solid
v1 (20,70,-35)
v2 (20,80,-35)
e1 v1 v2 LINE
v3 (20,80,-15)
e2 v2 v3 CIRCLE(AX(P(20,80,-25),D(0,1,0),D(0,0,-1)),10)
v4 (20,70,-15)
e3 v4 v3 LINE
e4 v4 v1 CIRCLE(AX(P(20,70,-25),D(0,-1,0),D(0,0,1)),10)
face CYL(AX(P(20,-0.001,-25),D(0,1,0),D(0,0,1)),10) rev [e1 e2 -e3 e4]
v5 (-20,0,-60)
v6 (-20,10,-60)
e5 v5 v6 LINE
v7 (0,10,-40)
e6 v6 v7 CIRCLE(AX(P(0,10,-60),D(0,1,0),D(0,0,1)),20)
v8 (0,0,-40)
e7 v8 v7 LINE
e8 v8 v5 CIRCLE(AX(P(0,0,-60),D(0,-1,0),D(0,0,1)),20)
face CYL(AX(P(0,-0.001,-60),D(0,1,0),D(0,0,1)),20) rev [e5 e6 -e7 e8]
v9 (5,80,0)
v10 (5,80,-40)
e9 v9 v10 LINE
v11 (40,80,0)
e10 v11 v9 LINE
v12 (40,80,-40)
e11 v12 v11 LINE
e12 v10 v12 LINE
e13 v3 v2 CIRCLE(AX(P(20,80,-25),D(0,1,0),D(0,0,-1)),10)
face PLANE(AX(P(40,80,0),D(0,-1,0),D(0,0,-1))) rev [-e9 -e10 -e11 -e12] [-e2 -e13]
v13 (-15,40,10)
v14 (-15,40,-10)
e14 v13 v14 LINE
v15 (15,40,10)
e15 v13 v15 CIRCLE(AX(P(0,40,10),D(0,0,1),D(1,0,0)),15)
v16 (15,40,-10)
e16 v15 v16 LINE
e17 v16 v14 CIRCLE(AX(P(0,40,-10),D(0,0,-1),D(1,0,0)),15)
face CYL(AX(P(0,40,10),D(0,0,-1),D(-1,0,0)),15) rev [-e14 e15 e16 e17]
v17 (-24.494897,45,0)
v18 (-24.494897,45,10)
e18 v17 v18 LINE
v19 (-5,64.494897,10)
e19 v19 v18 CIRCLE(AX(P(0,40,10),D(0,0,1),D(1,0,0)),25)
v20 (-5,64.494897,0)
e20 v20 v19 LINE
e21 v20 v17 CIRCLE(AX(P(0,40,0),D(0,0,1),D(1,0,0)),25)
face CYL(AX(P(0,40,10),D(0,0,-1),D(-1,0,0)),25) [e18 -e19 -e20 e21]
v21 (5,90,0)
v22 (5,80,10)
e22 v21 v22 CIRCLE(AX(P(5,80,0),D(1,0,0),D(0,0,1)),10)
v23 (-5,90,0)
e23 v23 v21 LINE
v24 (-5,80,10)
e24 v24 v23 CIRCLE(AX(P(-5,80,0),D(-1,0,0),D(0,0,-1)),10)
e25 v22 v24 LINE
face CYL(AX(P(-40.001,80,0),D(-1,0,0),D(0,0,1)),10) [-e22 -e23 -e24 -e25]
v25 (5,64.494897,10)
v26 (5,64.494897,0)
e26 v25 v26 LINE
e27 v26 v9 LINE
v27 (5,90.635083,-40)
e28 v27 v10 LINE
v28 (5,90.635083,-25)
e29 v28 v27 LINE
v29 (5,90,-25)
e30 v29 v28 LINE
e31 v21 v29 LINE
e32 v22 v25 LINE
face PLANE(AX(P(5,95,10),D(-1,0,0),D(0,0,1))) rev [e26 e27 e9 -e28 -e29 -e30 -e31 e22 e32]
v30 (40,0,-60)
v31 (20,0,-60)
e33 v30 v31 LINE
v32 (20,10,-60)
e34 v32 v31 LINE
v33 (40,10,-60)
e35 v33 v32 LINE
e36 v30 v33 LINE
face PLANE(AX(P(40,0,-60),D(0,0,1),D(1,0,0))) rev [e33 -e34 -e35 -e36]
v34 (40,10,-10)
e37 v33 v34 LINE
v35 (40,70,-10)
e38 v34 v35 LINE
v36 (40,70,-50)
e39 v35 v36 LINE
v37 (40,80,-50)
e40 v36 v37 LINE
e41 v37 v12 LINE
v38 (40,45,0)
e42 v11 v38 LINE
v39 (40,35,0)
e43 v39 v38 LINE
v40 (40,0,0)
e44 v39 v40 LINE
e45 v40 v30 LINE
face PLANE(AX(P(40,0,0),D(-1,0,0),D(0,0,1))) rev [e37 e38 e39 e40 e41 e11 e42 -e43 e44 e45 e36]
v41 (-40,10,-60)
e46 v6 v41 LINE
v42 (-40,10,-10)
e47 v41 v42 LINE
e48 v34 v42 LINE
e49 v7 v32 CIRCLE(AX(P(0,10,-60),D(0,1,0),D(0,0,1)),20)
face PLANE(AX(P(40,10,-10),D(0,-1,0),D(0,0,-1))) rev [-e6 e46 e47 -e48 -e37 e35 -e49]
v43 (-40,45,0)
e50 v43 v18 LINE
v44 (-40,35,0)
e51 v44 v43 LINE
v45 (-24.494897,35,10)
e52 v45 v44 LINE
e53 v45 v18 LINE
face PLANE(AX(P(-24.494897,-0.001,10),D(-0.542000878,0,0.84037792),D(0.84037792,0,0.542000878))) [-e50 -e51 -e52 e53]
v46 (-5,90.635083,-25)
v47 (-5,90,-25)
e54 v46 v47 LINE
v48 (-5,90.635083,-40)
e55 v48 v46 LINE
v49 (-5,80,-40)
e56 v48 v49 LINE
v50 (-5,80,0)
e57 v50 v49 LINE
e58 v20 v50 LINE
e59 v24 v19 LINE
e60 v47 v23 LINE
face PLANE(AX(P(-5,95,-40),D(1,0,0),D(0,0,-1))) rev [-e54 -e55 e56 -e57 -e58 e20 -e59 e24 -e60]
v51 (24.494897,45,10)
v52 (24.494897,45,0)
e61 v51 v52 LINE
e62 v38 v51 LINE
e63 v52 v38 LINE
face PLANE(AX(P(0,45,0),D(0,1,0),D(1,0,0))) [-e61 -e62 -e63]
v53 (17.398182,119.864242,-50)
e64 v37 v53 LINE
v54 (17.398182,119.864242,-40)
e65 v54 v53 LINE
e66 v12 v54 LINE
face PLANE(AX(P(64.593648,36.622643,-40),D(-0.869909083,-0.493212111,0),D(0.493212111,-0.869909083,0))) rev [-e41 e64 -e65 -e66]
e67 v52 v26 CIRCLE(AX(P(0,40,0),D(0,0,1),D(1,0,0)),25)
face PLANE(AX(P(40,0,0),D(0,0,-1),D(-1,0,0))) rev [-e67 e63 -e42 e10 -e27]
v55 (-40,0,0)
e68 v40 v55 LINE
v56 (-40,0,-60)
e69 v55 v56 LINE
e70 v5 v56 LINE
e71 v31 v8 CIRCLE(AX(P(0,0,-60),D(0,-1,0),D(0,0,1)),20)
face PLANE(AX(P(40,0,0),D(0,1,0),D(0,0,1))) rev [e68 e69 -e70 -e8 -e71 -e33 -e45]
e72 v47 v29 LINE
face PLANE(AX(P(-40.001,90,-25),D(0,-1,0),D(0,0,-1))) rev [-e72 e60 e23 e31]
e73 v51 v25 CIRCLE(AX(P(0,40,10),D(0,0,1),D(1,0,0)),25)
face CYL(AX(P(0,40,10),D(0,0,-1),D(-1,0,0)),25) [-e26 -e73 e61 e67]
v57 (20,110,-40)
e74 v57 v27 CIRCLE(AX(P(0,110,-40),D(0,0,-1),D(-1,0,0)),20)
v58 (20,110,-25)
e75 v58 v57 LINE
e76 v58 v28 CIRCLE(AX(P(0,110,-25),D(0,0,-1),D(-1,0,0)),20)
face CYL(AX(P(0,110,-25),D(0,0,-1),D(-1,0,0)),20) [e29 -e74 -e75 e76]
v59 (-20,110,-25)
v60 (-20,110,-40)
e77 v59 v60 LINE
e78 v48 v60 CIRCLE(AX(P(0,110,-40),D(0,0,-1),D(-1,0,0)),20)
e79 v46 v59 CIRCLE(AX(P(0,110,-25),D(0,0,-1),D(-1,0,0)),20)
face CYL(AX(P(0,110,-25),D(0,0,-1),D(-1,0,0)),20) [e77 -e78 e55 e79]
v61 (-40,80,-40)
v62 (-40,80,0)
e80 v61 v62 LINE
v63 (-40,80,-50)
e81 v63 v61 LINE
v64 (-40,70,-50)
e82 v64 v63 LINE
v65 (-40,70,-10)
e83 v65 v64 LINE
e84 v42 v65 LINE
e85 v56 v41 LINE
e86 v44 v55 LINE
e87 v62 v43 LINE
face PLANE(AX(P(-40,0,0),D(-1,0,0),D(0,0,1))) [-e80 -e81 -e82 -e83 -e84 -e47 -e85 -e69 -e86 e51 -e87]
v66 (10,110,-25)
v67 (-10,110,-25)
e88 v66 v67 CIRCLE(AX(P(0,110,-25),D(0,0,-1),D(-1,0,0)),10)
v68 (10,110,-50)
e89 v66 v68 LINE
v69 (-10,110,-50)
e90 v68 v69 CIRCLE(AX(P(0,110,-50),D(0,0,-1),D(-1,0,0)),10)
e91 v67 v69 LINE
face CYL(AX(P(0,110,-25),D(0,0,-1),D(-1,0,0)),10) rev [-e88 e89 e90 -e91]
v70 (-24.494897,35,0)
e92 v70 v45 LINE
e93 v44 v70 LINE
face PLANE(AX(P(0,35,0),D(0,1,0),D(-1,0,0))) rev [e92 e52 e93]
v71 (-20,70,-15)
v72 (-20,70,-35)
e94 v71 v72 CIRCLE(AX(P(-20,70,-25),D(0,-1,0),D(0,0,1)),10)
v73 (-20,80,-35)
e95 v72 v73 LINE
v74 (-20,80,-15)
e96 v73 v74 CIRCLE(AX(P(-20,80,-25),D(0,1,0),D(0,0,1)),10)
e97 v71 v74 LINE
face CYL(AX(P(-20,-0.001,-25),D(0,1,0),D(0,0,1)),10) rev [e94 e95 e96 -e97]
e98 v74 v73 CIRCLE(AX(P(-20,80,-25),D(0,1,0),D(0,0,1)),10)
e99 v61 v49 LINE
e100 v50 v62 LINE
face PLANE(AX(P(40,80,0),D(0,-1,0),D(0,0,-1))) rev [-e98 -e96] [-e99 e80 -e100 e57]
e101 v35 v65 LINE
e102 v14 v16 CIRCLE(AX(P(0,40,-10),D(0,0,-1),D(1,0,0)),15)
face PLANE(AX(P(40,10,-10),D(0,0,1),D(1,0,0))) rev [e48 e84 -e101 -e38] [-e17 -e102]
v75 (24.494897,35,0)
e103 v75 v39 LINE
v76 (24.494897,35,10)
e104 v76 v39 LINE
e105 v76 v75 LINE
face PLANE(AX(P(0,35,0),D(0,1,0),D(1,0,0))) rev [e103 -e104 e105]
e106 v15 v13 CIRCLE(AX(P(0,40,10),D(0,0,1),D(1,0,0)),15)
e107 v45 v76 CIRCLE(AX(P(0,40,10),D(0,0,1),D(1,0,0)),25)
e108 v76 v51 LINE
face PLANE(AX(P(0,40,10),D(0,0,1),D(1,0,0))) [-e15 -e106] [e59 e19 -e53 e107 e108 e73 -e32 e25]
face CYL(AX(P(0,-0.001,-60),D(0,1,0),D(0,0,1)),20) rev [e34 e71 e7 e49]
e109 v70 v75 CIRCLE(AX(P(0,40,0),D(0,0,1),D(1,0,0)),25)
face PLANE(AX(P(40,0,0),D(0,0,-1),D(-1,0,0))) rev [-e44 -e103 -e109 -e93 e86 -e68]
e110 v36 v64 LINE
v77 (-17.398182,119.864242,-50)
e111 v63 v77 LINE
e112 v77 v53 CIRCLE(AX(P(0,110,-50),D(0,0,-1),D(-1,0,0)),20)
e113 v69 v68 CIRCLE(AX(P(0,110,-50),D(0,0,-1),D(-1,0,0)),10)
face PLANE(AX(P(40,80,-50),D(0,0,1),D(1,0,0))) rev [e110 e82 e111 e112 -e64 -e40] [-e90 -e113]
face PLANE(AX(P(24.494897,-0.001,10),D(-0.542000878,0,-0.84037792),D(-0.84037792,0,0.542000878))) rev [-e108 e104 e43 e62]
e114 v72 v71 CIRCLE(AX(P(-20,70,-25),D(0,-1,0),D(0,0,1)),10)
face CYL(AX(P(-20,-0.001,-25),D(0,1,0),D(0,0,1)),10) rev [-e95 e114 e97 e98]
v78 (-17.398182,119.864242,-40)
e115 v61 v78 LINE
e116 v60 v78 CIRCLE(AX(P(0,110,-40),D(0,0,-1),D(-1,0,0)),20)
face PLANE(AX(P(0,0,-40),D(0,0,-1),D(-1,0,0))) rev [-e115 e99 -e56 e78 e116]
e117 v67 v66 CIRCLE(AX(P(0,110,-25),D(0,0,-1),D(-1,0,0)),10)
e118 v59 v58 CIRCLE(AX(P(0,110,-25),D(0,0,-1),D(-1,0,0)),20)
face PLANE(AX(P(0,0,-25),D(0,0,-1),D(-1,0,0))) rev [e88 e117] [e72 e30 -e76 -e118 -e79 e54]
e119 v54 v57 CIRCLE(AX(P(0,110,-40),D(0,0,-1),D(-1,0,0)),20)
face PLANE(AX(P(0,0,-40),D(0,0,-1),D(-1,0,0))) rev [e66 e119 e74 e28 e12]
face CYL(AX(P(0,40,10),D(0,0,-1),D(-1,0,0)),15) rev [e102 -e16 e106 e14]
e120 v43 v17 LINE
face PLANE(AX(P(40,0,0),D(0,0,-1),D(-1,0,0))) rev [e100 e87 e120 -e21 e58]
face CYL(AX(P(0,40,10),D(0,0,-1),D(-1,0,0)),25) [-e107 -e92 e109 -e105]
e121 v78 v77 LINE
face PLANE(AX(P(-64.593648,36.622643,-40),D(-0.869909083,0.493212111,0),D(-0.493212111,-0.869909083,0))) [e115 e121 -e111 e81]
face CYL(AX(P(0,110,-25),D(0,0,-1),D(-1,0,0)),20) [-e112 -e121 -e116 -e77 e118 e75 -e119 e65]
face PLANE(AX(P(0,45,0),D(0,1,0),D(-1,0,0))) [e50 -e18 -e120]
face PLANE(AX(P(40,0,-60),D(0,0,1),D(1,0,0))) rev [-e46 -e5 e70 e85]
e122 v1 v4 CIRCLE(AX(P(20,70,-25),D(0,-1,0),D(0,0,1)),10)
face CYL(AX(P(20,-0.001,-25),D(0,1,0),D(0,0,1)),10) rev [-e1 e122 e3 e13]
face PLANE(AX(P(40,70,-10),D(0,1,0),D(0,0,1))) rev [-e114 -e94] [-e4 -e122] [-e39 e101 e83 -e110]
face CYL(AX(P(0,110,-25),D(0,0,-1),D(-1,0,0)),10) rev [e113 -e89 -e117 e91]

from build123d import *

# Parameters (mm, degrees)
BASE_BRACKET_80MM_DEPTH   = 40
UPPER_LUG_PLATE_DEPTH     = 10
SKETCH2_3_R               = 20
SKETCH2_3_R_2             = 10
UPPER_LUG_HUB_DEPTH       = 25
FRONT_LUG_PROFILE_R       = 25
FRONT_LUG_PROFILE_R_2     = 15
FRONT_LUG_BOSS_DEPTH      = 10
FRONT_LUG_BORE_REACH      = 150.661
SKETCH4_2_R               = 15
CONNECTING_WEB_DEPTH      = 5
WEB_PAD_A_PROFILE_W       = 10
WEB_PAD_A_PROFILE_H       = 10
WEB_PAD_A_DEPTH           = 5
WEB_PAD_B_PROFILE_W       = 10
WEB_PAD_B_PROFILE_H       = 50
WEB_PAD_B_DEPTH           = 5
WEB_RELIEF_CUT_REACH      = 152.083
WEB_RELIEF_PROFILE_W      = 35
WEB_RELIEF_PROFILE_H      = 5
WEB_RELIEF_FILLET_R10_R   = 10
GUSSET_RIB_DEPTH          = 5
RIB_TRIM_CUT_REACH        = 113.467
RIB_PAD_A_DEPTH           = 5
RIB_PAD_B_DEPTH           = 5
LUG_CLEARANCE_CUT_REACH   = 154.971
RIB_NOTCH_CUT_DEPTH       = 10
UPPER_HUB_BORE_20_REACH   = 109.703
UPPER_HUB_BORE_PROFILE_R  = 10
BASE_ARC_CUTOUT_REACH     = 142
BASE_ARC_CUTOUT_PROFILE_R = 20


with BuildPart() as part:
    # Base Bracket Profile → Base Bracket 80mm (new, symmetric)
    with BuildSketch(Plane(origin=(0, 0, 0), x_dir=(0, 0, -1), z_dir=(1, 0, 0))):
        Polygon((0, 0), (60, 0), (60, 10), (10, 10), (10, 70), (50, 70), (50, 80), (0, 80), align=None)
    extrude(amount=BASE_BRACKET_80MM_DEPTH, both=True)

    # Upper Lug Profile → Upper Lug Plate (add)
    with BuildSketch(Plane(origin=(0, 0, -50), x_dir=(-1, 0, 0), z_dir=(0, 0, -1))):
        with BuildLine():
            Line((-40, 80), (0, 80))
            Line((0, 80), (0, 90))
            ThreePointArc((0, 90), (-17.281273745, 99.932349938), (-17.398181668, 119.864242224))
            Line((-17.398181668, 119.864242224), (-40, 80))
        make_face()
        with BuildLine():
            Line((0, 90), (0, 80))
            Line((0, 80), (40, 80))
            Line((40, 80), (17.398181668, 119.864242224))
            ThreePointArc((17.398181668, 119.864242224), (19.338609482, 115.100802223), (20, 110))
            ThreePointArc((20, 110), (14.142135624, 95.857864376), (0, 90))
        make_face()
    extrude(amount=-UPPER_LUG_PLATE_DEPTH)

    # Sketch2_3 → Upper Lug Hub (add)
    with BuildSketch(Plane(origin=(0, 0, -50), x_dir=(-1, 0, 0), z_dir=(0, 0, -1))):
        with Locations((0, 110)):
            Circle(SKETCH2_3_R)
        with Locations((0, 110)):
            Circle(SKETCH2_3_R_2, mode=Mode.SUBTRACT)
    extrude(amount=-UPPER_LUG_HUB_DEPTH)

    # Front Lug Profile → Front Lug Boss (add)
    with BuildSketch(Plane.XY):
        with Locations((0, 40)):
            Circle(FRONT_LUG_PROFILE_R)
        with Locations((0, 40)):
            Circle(FRONT_LUG_PROFILE_R_2, mode=Mode.SUBTRACT)
    extrude(amount=FRONT_LUG_BOSS_DEPTH)

    # Sketch4_2 → Front Lug Bore (cut, up to next)
    with BuildSketch(Plane.XY, mode=Mode.PRIVATE) as front_lug_bore_sk1:
        with Locations((0, 40)):
            Circle(SKETCH4_2_R)
    front_lug_bore_tool1 = extrude(front_lug_bore_sk1.sketch, amount=-FRONT_LUG_BORE_REACH, mode=Mode.PRIVATE) & part.part
    add(front_lug_bore_tool1.solids().sort_by_distance((0, 40, 0))[0], mode=Mode.SUBTRACT)



with BuildPart() as body_2:
    # Connecting Web Profile → Connecting Web (new, symmetric)
    with BuildSketch(Plane(origin=(0, 0, 0), x_dir=(0, 0, -1), z_dir=(1, 0, 0))):
        Polygon((-10, 66.461599877), (-10, 90), (40, 90), (40, 80), (0, 80), (0, 66.461599877), align=None)
    extrude(amount=CONNECTING_WEB_DEPTH, both=True)


with BuildPart() as body_3:
    # Web Pad A Profile → Web Pad A (new, symmetric)
    with BuildSketch(Plane.XZ.offset(-66.461599877)):
        with Locations((0, 5)):
            Rectangle(WEB_PAD_A_PROFILE_W, WEB_PAD_A_PROFILE_H)
    extrude(amount=WEB_PAD_A_DEPTH, both=True)


with BuildPart() as part_1:
    add(part.part)

    add(body_2.part)  # Web Pad B merges body 2
    # Web Pad B Profile → Web Pad B (add, symmetric)
    with BuildSketch(Plane(origin=(0, 90, 0), x_dir=(1, 0, 0), z_dir=(0, 1, 0))):
        with Locations((0, 15)):
            Rectangle(WEB_PAD_B_PROFILE_W, WEB_PAD_B_PROFILE_H)
    extrude(amount=WEB_PAD_B_DEPTH, both=True)

    # Combine Web Pads: union body 3
    add(body_3.part)

    # Web Relief Profile → Web Relief Cut (cut, up to next)
    with BuildSketch(Plane(origin=(5, 0, 0), x_dir=(0, 0, -1), z_dir=(1, 0, 0)), mode=Mode.PRIVATE) as web_relief_cut_sk1:
        with Locations((7.5, 92.5)):
            Rectangle(WEB_RELIEF_PROFILE_W, WEB_RELIEF_PROFILE_H)
    web_relief_cut_tool1 = extrude(web_relief_cut_sk1.sketch, amount=-WEB_RELIEF_CUT_REACH, mode=Mode.PRIVATE) & part_1.part
    add(web_relief_cut_tool1.solids().sort_by_distance((5, 92.5, -7.5))[0], mode=Mode.SUBTRACT)

    # Web Relief Fillet R10
    web_relief_fillet_r10_edges = [part_1.edges().sort_by_distance(p)[0] for p in [
        (0, 90, 10),
    ]]
    fillet(web_relief_fillet_r10_edges, radius=WEB_RELIEF_FILLET_R10_R)

    # Gusset Rib Path → Gusset Rib (add, symmetric)
    with BuildSketch(Plane(origin=(0, 40, 0), x_dir=(-1, 0, 0), z_dir=(0, -1, 0))):
        Polygon((-25, -10), (-40, 0), (-34.452998038, 8.320502943), (-19.452998038, -1.679497057), align=None)
    gusset_rib = extrude(amount=GUSSET_RIB_DEPTH, both=True)

    # Rib Trim Profile → Rib Trim Cut (cut, up to next)
    with BuildSketch(Plane(origin=(0, 45, 0), x_dir=(1, 0, 0), z_dir=(0, 1, 0)), mode=Mode.PRIVATE) as rib_trim_cut_sk1:
        Polygon((24.494897428, -10), (40, 0), (25, -10), align=None)
    rib_trim_cut_tool1 = extrude(rib_trim_cut_sk1.sketch, amount=-RIB_TRIM_CUT_REACH, mode=Mode.PRIVATE) & part_1.part
    rib_trim_cut = rib_trim_cut_tool1.solids().sort_by_distance((29.831632, 45, 6.666667))[0]
    add(rib_trim_cut, mode=Mode.SUBTRACT)

    # Rib Pad A Profile → Rib Pad A (add, symmetric)
    with BuildSketch(Plane(origin=(12.692307692, 0, -8.461538462), x_dir=(0.5547001962252294, 0, 0.8320502943378436), z_dir=(-0.8320502943378436, 0, 0.5547001962252294))):
        with BuildLine():
            Line((21.277421237, 35), (21.91421024, 35))
            Line((21.91421024, 35), (21.91421024, 37.248507099))
            add(Edge.make_bspline(
                [(21.277421237, 35), (21.688173728, 36.116205467), (21.91421024, 37.248507099)],
                knots=[2.940234733, 2.940234733, 2.940234733, 3.031309523, 3.031309523, 3.031309523], degree=2, weights=[1, 0.998963352, 1]))
        make_face()
    rib_pad_a = extrude(amount=RIB_PAD_A_DEPTH, both=True)

    # Rib Pad B Profile → Rib Pad B (add, symmetric)
    with BuildSketch(Plane(origin=(12.692307692, 0, -8.461538462), x_dir=(0.5547001962252294, 0, 0.8320502943378436), z_dir=(-0.8320502943378436, 0, 0.5547001962252294))):
        with BuildLine():
            Line((21.91421024, 42.751492901), (21.91421024, 45))
            Line((21.91421024, 45), (21.277421237, 45))
            add(Edge.make_bspline(
                [(21.91421024, 42.751492901), (21.688173728, 43.883794533), (21.277421237, 45)],
                knots=[3.251875784, 3.251875784, 3.251875784, 3.342950574, 3.342950574, 3.342950574], degree=2, weights=[1, 0.998963352, 1]))
        make_face()
    rib_pad_b = extrude(amount=RIB_PAD_B_DEPTH, both=True)

    # Lug Clearance Cut: up to this plane
    lug_clearance_cut_end = Plane(origin=(20.687872941, 35, 12.5456876), z_dir=(-0.5547001962252294, 0, -0.8320502943378436))
    # Lug Clearance Profile → Lug Clearance Cut (cut, up to the surface)
    with BuildSketch(Plane.XY.offset(10), mode=Mode.PRIVATE) as lug_clearance_cut_sk1:
        with BuildLine():
            Line((24.494897428, 37.216718732), (24.494897428, 35))
            ThreePointArc((24.494897428, 35), (-17.67766953, 22.32233047), (-5, 64.494897428))
            Line((-5, 64.494897428), (-5, 80))
            Line((-5, 80), (5, 80))
            Line((5, 80), (5, 64.494897428))
            ThreePointArc((5, 64.494897428), (17.67766953, 57.67766953), (24.494897428, 45))
            Line((24.494897428, 45), (24.494897428, 37.216718732))
        make_face()
    lug_clearance_cut_tool1 = split(extrude(lug_clearance_cut_sk1.sketch, amount=LUG_CLEARANCE_CUT_REACH, mode=Mode.PRIVATE), bisect_by=lug_clearance_cut_end, keep=Keep.BOTH, mode=Mode.PRIVATE)
    lug_clearance_cut = lug_clearance_cut_tool1.solids().sort_by_distance((-0.039461, 42.32819, 10))[0]
    add(lug_clearance_cut, mode=Mode.SUBTRACT)

    # Rib Notch Profile → Rib Notch Cut (cut)
    with BuildSketch(Plane.XZ.offset(-35)):
        Polygon((24.848124412, 9.772186619), (24.494897428, 10), (24.494897428, 10.007671275), align=None)
    rib_notch_cut = extrude(amount=-RIB_NOTCH_CUT_DEPTH, mode=Mode.SUBTRACT)

    # Rib Features Mirror: Gusset Rib, Rib Trim Cut, Rib Pad A, Rib Pad B, Lug Clearance Cut, Rib Notch Cut across plane
    add(gusset_rib.mirror(Plane(origin=(0, 0, 0), x_dir=(0, 0, 1), z_dir=(1, 0, 0))))
    add(rib_trim_cut.mirror(Plane(origin=(0, 0, 0), x_dir=(0, 0, 1), z_dir=(1, 0, 0))), mode=Mode.SUBTRACT)
    add(rib_pad_a.mirror(Plane(origin=(0, 0, 0), x_dir=(0, 0, 1), z_dir=(1, 0, 0))))
    add(rib_pad_b.mirror(Plane(origin=(0, 0, 0), x_dir=(0, 0, 1), z_dir=(1, 0, 0))))
    add(lug_clearance_cut.mirror(Plane(origin=(0, 0, 0), x_dir=(0, 0, 1), z_dir=(1, 0, 0))), mode=Mode.SUBTRACT)
    add(rib_notch_cut.mirror(Plane(origin=(0, 0, 0), x_dir=(0, 0, 1), z_dir=(1, 0, 0))), mode=Mode.SUBTRACT)

    # Upper Hub Bore Profile → Upper Hub Bore _20 (cut, up to next)
    with BuildSketch(Plane(origin=(0, 80, 0), x_dir=(1, 0, 0), z_dir=(0, 1, 0)), mode=Mode.PRIVATE) as upper_hub_bore_20_sk1:
        with Locations(Location((-20, 25, 0), (0, 0, 270))):
            Circle(UPPER_HUB_BORE_PROFILE_R)
    upper_hub_bore_20_tool1 = extrude(upper_hub_bore_20_sk1.sketch, amount=-UPPER_HUB_BORE_20_REACH, mode=Mode.PRIVATE) & part_1.part
    # Upper Hub Bore Profile → Upper Hub Bore _20 (cut, up to next)
    with BuildSketch(Plane(origin=(0, 80, 0), x_dir=(1, 0, 0), z_dir=(0, 1, 0)), mode=Mode.PRIVATE) as upper_hub_bore_20_sk2:
        with Locations(Location((20, 25, 0), (0, 0, 270))):
            Circle(UPPER_HUB_BORE_PROFILE_R)
    upper_hub_bore_20_tool2 = extrude(upper_hub_bore_20_sk2.sketch, amount=-UPPER_HUB_BORE_20_REACH, mode=Mode.PRIVATE) & part_1.part
    add(upper_hub_bore_20_tool1.solids().sort_by_distance((-20, 80, -25))[0], mode=Mode.SUBTRACT)
    add(upper_hub_bore_20_tool2.solids().sort_by_distance((20, 80, -25))[0], mode=Mode.SUBTRACT)

    # Base Arc Cutout Profile → Base Arc Cutout (cut, up to next)
    with BuildSketch(Plane(origin=(0, 10, 0), x_dir=(1, 0, 0), z_dir=(0, 1, 0)), mode=Mode.PRIVATE) as base_arc_cutout_sk1:
        with Locations((0, 60)):
            Circle(BASE_ARC_CUTOUT_PROFILE_R)
    base_arc_cutout_tool1 = extrude(base_arc_cutout_sk1.sketch, amount=-BASE_ARC_CUTOUT_REACH, mode=Mode.PRIVATE) & part_1.part
    add(base_arc_cutout_tool1.solids().sort_by_distance((0, 10, -60))[0], mode=Mode.SUBTRACT)


solid = part_1.part
